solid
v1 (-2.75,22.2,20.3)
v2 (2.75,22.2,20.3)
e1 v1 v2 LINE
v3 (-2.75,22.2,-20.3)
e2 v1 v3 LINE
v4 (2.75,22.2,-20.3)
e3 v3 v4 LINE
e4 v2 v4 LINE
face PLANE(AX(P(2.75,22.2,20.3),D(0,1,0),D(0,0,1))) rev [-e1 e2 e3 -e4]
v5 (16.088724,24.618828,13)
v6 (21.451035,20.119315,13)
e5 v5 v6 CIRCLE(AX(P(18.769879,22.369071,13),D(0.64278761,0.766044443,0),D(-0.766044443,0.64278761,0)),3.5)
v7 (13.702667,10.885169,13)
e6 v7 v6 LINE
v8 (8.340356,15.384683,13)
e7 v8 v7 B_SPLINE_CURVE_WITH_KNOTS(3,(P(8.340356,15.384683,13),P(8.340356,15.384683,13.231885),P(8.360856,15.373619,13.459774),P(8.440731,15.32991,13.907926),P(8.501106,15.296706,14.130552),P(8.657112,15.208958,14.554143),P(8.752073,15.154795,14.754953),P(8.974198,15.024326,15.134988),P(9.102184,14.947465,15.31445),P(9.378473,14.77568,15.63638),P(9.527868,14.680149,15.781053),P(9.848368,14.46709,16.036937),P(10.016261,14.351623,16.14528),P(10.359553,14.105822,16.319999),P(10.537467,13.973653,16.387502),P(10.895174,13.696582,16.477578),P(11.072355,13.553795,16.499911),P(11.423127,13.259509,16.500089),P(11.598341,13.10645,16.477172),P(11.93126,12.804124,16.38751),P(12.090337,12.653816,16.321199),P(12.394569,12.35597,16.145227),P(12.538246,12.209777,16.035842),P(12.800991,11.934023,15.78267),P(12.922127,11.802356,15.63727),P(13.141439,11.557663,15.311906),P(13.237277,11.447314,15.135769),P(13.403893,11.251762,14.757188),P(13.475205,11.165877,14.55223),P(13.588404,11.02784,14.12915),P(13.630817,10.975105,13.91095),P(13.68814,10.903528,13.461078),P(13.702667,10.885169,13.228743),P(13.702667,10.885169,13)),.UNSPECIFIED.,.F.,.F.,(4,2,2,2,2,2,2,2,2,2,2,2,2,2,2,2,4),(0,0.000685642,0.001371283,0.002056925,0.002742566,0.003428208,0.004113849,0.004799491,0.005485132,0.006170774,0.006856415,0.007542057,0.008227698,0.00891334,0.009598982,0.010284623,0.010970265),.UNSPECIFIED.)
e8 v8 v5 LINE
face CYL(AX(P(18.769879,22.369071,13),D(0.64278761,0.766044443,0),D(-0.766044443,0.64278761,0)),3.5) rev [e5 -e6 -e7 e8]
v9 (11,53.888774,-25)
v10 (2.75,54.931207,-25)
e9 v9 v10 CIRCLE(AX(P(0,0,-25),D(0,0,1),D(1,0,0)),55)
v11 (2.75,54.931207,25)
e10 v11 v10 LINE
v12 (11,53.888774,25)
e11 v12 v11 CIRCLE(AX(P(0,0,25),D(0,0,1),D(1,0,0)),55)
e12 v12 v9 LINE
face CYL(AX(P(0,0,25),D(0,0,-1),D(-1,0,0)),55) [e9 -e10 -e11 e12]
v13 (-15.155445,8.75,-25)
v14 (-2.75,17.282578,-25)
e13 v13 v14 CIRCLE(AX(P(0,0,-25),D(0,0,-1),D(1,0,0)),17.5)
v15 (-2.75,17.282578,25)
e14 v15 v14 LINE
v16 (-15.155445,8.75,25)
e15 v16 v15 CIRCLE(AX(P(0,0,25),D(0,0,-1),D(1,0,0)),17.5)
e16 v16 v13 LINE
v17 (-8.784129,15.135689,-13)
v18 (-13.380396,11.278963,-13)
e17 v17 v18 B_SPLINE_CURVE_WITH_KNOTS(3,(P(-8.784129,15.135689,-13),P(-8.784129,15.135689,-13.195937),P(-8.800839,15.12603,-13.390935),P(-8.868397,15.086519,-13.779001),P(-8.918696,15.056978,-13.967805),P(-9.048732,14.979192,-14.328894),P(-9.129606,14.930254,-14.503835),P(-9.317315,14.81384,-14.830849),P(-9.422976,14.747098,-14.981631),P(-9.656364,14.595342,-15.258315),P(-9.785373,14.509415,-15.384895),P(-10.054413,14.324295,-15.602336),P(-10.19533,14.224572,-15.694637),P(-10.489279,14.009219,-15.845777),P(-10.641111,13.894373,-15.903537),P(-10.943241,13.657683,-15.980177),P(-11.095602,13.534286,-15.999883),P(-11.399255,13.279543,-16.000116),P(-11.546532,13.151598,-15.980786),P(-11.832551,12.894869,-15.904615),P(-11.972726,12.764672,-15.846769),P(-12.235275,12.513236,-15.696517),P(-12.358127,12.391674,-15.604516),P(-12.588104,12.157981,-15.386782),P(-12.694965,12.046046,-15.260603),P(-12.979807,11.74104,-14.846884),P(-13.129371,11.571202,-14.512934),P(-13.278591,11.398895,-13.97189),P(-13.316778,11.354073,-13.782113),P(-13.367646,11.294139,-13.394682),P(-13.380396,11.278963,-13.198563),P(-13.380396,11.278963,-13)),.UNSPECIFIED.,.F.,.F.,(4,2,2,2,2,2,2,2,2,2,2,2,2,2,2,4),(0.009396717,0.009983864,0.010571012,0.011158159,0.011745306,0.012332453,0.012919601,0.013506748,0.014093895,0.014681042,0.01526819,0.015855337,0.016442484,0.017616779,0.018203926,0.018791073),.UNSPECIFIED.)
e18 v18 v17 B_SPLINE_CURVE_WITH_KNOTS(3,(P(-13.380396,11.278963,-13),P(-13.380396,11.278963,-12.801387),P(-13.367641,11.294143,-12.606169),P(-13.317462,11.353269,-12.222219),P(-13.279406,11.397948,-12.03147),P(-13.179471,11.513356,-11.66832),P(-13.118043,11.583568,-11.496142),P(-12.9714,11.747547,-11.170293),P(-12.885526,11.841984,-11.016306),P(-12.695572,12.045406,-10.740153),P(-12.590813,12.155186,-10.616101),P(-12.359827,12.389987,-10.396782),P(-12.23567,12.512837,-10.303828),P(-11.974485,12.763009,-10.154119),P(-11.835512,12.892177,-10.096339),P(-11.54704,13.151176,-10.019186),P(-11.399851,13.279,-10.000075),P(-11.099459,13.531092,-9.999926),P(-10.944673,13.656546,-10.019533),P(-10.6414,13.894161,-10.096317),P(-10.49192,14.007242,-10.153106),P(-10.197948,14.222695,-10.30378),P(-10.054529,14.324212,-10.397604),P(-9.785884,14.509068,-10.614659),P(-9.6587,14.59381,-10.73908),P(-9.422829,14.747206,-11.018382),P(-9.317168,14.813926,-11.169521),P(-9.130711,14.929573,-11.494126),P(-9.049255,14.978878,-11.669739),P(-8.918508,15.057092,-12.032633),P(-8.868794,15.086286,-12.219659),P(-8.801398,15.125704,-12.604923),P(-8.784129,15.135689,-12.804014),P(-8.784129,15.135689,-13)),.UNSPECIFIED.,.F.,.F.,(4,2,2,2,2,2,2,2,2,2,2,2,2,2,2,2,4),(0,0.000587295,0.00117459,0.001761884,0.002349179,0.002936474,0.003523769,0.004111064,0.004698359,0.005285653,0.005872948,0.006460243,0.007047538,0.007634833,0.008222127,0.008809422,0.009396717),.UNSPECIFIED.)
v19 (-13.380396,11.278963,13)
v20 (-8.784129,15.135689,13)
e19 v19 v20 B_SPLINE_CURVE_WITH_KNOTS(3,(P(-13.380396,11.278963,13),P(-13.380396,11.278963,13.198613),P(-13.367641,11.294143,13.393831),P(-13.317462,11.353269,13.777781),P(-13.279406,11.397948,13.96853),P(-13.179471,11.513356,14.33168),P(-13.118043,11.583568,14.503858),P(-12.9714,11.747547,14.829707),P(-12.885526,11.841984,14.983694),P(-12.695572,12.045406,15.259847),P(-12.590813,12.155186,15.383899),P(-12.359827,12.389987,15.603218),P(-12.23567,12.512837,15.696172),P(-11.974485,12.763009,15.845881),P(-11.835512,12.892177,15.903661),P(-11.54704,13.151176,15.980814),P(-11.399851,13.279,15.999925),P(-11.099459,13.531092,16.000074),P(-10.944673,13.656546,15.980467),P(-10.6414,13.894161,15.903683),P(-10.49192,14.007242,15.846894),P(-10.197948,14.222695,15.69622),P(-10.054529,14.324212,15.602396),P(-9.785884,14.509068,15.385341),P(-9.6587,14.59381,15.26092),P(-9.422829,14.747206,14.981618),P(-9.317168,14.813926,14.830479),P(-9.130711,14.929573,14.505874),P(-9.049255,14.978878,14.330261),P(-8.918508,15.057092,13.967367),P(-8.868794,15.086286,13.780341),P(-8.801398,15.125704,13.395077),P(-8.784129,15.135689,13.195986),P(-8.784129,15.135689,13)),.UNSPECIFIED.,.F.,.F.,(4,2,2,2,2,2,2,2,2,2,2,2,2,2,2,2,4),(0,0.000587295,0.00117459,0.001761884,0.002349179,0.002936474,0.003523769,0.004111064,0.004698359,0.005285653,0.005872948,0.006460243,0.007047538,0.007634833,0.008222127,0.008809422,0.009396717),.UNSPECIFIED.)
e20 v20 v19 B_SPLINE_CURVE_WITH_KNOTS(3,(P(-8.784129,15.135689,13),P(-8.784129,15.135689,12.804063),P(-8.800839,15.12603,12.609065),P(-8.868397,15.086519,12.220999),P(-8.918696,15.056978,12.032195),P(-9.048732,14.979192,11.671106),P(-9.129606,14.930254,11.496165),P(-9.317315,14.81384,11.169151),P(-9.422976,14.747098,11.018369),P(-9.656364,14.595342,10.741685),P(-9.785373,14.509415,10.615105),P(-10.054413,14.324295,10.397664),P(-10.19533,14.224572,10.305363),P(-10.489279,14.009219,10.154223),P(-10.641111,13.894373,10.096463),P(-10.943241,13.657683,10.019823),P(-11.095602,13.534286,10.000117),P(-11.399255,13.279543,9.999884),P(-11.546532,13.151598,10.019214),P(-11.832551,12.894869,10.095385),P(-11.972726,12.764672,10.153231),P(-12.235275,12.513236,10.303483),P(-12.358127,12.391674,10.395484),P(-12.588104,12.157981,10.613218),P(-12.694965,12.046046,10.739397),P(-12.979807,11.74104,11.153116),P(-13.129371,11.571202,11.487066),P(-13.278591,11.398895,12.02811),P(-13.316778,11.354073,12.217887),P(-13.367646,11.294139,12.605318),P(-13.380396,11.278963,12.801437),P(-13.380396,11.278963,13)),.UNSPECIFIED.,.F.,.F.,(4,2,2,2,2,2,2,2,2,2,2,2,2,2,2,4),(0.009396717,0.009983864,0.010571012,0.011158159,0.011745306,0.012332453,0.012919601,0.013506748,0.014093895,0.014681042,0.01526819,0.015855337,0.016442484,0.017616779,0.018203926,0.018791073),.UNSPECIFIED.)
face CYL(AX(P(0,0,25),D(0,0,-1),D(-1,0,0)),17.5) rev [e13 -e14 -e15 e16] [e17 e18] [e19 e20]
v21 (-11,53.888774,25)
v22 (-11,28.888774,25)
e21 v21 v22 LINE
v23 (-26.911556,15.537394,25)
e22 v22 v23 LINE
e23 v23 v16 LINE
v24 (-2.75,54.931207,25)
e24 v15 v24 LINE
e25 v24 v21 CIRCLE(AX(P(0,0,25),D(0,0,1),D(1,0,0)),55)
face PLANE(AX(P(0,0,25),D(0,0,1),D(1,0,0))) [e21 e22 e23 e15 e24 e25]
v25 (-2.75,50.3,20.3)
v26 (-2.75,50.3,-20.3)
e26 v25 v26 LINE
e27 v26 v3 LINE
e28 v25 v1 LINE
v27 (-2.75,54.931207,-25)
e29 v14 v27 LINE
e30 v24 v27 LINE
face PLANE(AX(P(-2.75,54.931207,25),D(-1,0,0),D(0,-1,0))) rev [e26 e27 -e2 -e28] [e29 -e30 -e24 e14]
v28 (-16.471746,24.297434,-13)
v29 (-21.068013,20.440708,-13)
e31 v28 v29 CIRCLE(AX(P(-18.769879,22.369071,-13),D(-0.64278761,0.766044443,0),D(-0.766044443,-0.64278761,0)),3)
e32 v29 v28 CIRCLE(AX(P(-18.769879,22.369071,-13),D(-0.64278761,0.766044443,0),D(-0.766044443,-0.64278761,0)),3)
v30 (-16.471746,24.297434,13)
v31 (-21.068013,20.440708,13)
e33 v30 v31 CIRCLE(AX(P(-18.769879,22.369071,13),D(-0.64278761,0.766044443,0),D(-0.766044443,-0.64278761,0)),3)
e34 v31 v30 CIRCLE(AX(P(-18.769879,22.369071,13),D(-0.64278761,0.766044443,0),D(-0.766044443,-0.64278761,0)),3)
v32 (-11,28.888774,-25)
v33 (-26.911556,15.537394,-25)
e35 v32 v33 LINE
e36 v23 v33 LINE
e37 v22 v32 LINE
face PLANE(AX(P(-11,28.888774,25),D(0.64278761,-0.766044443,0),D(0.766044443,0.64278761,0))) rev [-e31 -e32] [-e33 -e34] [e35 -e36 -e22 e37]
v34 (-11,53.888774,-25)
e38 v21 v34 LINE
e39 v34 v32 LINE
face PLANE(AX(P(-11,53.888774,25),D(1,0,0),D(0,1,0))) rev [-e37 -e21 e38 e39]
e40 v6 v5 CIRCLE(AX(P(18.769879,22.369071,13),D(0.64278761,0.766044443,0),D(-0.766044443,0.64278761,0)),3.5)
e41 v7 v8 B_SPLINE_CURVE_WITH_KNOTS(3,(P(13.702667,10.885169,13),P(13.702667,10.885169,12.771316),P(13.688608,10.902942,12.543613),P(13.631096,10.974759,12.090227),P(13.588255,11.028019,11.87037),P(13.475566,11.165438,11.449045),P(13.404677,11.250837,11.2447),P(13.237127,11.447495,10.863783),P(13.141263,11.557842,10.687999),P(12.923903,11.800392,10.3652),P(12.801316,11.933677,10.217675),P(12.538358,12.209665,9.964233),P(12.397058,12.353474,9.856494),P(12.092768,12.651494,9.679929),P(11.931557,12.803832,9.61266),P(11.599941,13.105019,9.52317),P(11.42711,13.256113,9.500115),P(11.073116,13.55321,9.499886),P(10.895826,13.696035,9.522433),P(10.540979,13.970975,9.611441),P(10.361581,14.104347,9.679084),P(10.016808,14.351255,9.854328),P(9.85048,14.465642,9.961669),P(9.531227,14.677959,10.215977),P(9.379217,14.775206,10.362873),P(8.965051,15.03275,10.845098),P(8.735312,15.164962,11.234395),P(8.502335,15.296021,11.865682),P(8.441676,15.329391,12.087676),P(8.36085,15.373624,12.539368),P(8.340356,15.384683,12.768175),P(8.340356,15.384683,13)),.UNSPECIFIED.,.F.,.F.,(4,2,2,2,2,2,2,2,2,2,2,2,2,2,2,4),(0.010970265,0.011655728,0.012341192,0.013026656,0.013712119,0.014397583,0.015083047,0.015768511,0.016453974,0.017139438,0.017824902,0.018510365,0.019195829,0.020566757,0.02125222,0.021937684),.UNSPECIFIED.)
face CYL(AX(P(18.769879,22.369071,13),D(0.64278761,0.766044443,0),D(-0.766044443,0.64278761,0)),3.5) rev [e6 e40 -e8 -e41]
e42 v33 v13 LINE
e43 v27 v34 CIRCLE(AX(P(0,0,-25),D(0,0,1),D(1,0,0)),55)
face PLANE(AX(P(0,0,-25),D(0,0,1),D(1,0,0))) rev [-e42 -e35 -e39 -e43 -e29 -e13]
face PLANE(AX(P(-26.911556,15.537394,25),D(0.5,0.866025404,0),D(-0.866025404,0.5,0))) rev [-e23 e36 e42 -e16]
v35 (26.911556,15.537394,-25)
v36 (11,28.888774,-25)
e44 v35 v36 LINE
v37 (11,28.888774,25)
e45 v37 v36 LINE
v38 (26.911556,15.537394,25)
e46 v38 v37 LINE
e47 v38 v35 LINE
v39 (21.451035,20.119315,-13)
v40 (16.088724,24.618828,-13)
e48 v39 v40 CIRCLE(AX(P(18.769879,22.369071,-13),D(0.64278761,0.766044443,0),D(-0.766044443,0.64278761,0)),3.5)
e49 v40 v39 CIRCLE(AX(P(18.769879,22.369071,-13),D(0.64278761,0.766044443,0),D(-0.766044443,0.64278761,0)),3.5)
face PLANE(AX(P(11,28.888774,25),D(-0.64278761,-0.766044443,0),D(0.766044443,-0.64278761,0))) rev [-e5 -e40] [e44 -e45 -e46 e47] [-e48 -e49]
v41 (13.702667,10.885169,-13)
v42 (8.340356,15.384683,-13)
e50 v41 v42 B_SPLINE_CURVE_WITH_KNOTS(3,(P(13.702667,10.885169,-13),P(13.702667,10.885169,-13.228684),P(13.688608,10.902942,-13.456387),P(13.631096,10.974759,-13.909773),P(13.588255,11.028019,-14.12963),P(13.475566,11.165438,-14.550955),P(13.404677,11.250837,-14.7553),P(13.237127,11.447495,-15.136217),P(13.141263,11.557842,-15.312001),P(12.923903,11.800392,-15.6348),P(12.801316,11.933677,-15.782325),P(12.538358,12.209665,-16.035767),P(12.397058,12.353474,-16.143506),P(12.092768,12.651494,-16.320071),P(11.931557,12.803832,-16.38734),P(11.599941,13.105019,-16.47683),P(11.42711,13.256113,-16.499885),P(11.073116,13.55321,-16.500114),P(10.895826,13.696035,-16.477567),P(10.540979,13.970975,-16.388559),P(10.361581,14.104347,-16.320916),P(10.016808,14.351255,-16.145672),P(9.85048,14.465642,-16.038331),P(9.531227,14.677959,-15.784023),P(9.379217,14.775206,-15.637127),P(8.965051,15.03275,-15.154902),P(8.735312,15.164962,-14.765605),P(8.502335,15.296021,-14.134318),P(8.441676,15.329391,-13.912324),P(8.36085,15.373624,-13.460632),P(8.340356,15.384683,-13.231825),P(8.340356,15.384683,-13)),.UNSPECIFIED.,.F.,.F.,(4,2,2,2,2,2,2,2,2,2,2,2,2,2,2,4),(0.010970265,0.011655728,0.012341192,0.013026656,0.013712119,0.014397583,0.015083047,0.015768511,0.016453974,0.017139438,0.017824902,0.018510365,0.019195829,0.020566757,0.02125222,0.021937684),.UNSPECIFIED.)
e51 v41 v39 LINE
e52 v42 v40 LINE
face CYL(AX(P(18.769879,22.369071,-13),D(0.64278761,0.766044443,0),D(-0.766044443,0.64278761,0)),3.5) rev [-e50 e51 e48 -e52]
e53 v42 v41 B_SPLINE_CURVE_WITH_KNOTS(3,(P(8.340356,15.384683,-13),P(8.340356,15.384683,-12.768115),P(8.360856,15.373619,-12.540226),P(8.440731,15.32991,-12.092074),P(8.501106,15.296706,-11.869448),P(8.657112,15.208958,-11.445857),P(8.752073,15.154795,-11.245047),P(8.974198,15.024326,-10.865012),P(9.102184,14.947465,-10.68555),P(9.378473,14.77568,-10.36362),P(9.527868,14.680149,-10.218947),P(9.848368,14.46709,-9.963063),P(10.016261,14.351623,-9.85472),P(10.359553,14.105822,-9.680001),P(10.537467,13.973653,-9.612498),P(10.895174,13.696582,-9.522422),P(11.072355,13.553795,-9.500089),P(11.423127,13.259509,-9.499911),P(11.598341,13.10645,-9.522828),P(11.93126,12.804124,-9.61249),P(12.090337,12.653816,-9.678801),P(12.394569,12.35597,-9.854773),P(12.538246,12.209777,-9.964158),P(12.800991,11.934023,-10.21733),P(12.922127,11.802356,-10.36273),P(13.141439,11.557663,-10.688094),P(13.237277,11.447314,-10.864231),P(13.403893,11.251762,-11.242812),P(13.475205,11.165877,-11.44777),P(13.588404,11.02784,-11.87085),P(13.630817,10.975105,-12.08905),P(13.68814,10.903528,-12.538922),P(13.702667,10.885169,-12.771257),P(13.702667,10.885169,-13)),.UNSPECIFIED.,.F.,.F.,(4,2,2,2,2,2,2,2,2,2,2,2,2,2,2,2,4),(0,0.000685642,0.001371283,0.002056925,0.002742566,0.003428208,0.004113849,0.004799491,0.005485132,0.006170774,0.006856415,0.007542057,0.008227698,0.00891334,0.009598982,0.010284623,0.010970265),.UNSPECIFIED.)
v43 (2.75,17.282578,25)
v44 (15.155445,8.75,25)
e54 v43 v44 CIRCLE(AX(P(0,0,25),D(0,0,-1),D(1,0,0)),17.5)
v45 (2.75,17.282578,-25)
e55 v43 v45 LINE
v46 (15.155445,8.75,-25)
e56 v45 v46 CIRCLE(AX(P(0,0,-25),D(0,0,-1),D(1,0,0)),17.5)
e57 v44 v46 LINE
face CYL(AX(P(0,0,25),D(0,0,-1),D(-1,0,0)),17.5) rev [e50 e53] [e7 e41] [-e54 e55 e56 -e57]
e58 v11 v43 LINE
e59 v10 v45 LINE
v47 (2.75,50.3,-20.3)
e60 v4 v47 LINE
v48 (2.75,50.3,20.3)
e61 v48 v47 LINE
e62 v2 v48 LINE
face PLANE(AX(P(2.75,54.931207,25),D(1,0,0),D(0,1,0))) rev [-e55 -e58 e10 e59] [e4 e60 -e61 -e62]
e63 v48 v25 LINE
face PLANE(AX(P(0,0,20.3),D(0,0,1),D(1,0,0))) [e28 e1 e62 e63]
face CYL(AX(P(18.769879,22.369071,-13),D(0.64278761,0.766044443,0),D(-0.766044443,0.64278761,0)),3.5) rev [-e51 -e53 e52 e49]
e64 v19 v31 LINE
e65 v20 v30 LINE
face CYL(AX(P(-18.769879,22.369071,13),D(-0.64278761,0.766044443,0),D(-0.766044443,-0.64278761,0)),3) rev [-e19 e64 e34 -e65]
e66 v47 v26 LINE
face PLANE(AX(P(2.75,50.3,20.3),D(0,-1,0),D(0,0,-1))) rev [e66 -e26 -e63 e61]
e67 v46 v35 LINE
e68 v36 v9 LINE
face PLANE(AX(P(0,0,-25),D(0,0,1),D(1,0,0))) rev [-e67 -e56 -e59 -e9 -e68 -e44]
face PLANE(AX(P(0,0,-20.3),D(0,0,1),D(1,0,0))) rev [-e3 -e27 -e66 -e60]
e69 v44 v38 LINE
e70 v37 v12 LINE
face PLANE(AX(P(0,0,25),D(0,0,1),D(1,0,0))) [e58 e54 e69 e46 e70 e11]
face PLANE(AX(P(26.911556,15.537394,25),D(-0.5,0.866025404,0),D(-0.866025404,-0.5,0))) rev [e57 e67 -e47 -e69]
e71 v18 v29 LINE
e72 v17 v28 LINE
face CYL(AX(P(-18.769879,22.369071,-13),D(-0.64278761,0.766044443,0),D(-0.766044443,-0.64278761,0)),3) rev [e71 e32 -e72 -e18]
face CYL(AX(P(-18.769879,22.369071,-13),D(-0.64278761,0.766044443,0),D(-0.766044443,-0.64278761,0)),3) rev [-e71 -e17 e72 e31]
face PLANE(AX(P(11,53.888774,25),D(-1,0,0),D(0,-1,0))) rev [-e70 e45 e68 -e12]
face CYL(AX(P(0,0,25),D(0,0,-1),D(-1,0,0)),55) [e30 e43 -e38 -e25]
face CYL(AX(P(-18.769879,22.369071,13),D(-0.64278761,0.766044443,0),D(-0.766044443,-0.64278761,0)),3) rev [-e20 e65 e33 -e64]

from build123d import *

# Parameters (mm, degrees)
BOSS_EXTRUDE1_DEPTH                   = 25
BOSS_EXTRUDE1_2_DEPTH                 = 25
SKETCH2_W                             = 5.5
SKETCH2_H                             = 28.1
BOSS_EXTRUDE2_DEPTH                   = 20.3
F_6_0MM_BLIND_DOWEL_HOLE1_D           = 6
F_6_0MM_BLIND_DOWEL_HOLE1_ON_FACE_2_D = 6
F_6_0MM_BLIND_DOWEL_HOLE2_D           = 7
F_6_0MM_BLIND_DOWEL_HOLE2_ON_FACE_2_D = 7


with BuildPart() as part:
    # Sketch1 → Boss-Extrude1 (new, symmetric)
    with BuildSketch(Plane.XY):
        with BuildLine():
            Line((-2.75, 54.931206977), (-2.75, 17.282577933))
            ThreePointArc((-2.75, 17.282577933), (-9.917280768, 14.418652578), (-15.155444566, 8.75))
            Line((-15.155444566, 8.75), (-26.911555625, 15.537393885))
            Line((-26.911555625, 15.537393885), (-11, 28.888774341))
            Line((-11, 28.888774341), (-11, 53.888774341))
            ThreePointArc((-11, 53.888774341), (-6.894729251, 54.566131515), (-2.75, 54.931206977))
        make_face()
    extrude(amount=BOSS_EXTRUDE1_DEPTH, both=True)



with BuildPart() as body_2:
    # Sketch1 → Boss-Extrude1 2 (new, symmetric)
    with BuildSketch(Plane.XY):
        with BuildLine():
            Line((11, 28.888774341), (26.911555625, 15.537393885))
            Line((26.911555625, 15.537393885), (15.155444566, 8.75))
            ThreePointArc((15.155444566, 8.75), (9.917280768, 14.418652578), (2.75, 17.282577933))
            Line((2.75, 17.282577933), (2.75, 54.931206977))
            ThreePointArc((2.75, 54.931206977), (6.894729251, 54.566131515), (11, 53.888774341))
            Line((11, 53.888774341), (11, 28.888774341))
        make_face()
    extrude(amount=BOSS_EXTRUDE1_2_DEPTH, both=True)


with BuildPart() as part_1:
    add(part.part)

    add(body_2.part)  # Boss-Extrude2 merges body 2
    # Sketch2 → Boss-Extrude2 (add, symmetric)
    with BuildSketch(Plane.XY):
        with Locations((0, 36.25)):
            Rectangle(SKETCH2_W, SKETCH2_H)
    extrude(amount=BOSS_EXTRUDE2_DEPTH, both=True)

    # Ø6.0mm Blind Dowel Hole1 (through all)
    with Locations(Plane(origin=(-18.769879496, 22.369071322, 13), x_dir=(0.766044443119, 0.642787609687, 0), z_dir=(-0.642787609687, 0.766044443119, 0))):
        with Locations((0, 0)):
            Hole(F_6_0MM_BLIND_DOWEL_HOLE1_D / 2)

    # Ø6.0mm Blind Dowel Hole1 on face 2 (through all)
    with Locations(Plane(origin=(-18.769879496, 22.369071322, -13), x_dir=(0.766044067841, 0.642788056925, 0), z_dir=(-0.642788056925, 0.766044067841, 0))):
        with Locations((0, 0)):
            Hole(F_6_0MM_BLIND_DOWEL_HOLE1_ON_FACE_2_D / 2)

    # Ø6.0mm Blind Dowel Hole2 (through all)
    with Locations(Plane(origin=(18.769879496, 22.369071322, 13), x_dir=(0.766044443119, -0.642787609687, 0), z_dir=(0.642787609687, 0.766044443119, 0))):
        with Locations((0, 0)):
            Hole(F_6_0MM_BLIND_DOWEL_HOLE2_D / 2)

    # Ø6.0mm Blind Dowel Hole2 on face 2 (through all)
    with Locations(Plane(origin=(18.769879496, 22.369071322, -13), x_dir=(0.766044067841, -0.642788056925, 0), z_dir=(0.642788056925, 0.766044067841, 0))):
        with Locations((0, 0)):
            Hole(F_6_0MM_BLIND_DOWEL_HOLE2_ON_FACE_2_D / 2)


solid = part_1.part
